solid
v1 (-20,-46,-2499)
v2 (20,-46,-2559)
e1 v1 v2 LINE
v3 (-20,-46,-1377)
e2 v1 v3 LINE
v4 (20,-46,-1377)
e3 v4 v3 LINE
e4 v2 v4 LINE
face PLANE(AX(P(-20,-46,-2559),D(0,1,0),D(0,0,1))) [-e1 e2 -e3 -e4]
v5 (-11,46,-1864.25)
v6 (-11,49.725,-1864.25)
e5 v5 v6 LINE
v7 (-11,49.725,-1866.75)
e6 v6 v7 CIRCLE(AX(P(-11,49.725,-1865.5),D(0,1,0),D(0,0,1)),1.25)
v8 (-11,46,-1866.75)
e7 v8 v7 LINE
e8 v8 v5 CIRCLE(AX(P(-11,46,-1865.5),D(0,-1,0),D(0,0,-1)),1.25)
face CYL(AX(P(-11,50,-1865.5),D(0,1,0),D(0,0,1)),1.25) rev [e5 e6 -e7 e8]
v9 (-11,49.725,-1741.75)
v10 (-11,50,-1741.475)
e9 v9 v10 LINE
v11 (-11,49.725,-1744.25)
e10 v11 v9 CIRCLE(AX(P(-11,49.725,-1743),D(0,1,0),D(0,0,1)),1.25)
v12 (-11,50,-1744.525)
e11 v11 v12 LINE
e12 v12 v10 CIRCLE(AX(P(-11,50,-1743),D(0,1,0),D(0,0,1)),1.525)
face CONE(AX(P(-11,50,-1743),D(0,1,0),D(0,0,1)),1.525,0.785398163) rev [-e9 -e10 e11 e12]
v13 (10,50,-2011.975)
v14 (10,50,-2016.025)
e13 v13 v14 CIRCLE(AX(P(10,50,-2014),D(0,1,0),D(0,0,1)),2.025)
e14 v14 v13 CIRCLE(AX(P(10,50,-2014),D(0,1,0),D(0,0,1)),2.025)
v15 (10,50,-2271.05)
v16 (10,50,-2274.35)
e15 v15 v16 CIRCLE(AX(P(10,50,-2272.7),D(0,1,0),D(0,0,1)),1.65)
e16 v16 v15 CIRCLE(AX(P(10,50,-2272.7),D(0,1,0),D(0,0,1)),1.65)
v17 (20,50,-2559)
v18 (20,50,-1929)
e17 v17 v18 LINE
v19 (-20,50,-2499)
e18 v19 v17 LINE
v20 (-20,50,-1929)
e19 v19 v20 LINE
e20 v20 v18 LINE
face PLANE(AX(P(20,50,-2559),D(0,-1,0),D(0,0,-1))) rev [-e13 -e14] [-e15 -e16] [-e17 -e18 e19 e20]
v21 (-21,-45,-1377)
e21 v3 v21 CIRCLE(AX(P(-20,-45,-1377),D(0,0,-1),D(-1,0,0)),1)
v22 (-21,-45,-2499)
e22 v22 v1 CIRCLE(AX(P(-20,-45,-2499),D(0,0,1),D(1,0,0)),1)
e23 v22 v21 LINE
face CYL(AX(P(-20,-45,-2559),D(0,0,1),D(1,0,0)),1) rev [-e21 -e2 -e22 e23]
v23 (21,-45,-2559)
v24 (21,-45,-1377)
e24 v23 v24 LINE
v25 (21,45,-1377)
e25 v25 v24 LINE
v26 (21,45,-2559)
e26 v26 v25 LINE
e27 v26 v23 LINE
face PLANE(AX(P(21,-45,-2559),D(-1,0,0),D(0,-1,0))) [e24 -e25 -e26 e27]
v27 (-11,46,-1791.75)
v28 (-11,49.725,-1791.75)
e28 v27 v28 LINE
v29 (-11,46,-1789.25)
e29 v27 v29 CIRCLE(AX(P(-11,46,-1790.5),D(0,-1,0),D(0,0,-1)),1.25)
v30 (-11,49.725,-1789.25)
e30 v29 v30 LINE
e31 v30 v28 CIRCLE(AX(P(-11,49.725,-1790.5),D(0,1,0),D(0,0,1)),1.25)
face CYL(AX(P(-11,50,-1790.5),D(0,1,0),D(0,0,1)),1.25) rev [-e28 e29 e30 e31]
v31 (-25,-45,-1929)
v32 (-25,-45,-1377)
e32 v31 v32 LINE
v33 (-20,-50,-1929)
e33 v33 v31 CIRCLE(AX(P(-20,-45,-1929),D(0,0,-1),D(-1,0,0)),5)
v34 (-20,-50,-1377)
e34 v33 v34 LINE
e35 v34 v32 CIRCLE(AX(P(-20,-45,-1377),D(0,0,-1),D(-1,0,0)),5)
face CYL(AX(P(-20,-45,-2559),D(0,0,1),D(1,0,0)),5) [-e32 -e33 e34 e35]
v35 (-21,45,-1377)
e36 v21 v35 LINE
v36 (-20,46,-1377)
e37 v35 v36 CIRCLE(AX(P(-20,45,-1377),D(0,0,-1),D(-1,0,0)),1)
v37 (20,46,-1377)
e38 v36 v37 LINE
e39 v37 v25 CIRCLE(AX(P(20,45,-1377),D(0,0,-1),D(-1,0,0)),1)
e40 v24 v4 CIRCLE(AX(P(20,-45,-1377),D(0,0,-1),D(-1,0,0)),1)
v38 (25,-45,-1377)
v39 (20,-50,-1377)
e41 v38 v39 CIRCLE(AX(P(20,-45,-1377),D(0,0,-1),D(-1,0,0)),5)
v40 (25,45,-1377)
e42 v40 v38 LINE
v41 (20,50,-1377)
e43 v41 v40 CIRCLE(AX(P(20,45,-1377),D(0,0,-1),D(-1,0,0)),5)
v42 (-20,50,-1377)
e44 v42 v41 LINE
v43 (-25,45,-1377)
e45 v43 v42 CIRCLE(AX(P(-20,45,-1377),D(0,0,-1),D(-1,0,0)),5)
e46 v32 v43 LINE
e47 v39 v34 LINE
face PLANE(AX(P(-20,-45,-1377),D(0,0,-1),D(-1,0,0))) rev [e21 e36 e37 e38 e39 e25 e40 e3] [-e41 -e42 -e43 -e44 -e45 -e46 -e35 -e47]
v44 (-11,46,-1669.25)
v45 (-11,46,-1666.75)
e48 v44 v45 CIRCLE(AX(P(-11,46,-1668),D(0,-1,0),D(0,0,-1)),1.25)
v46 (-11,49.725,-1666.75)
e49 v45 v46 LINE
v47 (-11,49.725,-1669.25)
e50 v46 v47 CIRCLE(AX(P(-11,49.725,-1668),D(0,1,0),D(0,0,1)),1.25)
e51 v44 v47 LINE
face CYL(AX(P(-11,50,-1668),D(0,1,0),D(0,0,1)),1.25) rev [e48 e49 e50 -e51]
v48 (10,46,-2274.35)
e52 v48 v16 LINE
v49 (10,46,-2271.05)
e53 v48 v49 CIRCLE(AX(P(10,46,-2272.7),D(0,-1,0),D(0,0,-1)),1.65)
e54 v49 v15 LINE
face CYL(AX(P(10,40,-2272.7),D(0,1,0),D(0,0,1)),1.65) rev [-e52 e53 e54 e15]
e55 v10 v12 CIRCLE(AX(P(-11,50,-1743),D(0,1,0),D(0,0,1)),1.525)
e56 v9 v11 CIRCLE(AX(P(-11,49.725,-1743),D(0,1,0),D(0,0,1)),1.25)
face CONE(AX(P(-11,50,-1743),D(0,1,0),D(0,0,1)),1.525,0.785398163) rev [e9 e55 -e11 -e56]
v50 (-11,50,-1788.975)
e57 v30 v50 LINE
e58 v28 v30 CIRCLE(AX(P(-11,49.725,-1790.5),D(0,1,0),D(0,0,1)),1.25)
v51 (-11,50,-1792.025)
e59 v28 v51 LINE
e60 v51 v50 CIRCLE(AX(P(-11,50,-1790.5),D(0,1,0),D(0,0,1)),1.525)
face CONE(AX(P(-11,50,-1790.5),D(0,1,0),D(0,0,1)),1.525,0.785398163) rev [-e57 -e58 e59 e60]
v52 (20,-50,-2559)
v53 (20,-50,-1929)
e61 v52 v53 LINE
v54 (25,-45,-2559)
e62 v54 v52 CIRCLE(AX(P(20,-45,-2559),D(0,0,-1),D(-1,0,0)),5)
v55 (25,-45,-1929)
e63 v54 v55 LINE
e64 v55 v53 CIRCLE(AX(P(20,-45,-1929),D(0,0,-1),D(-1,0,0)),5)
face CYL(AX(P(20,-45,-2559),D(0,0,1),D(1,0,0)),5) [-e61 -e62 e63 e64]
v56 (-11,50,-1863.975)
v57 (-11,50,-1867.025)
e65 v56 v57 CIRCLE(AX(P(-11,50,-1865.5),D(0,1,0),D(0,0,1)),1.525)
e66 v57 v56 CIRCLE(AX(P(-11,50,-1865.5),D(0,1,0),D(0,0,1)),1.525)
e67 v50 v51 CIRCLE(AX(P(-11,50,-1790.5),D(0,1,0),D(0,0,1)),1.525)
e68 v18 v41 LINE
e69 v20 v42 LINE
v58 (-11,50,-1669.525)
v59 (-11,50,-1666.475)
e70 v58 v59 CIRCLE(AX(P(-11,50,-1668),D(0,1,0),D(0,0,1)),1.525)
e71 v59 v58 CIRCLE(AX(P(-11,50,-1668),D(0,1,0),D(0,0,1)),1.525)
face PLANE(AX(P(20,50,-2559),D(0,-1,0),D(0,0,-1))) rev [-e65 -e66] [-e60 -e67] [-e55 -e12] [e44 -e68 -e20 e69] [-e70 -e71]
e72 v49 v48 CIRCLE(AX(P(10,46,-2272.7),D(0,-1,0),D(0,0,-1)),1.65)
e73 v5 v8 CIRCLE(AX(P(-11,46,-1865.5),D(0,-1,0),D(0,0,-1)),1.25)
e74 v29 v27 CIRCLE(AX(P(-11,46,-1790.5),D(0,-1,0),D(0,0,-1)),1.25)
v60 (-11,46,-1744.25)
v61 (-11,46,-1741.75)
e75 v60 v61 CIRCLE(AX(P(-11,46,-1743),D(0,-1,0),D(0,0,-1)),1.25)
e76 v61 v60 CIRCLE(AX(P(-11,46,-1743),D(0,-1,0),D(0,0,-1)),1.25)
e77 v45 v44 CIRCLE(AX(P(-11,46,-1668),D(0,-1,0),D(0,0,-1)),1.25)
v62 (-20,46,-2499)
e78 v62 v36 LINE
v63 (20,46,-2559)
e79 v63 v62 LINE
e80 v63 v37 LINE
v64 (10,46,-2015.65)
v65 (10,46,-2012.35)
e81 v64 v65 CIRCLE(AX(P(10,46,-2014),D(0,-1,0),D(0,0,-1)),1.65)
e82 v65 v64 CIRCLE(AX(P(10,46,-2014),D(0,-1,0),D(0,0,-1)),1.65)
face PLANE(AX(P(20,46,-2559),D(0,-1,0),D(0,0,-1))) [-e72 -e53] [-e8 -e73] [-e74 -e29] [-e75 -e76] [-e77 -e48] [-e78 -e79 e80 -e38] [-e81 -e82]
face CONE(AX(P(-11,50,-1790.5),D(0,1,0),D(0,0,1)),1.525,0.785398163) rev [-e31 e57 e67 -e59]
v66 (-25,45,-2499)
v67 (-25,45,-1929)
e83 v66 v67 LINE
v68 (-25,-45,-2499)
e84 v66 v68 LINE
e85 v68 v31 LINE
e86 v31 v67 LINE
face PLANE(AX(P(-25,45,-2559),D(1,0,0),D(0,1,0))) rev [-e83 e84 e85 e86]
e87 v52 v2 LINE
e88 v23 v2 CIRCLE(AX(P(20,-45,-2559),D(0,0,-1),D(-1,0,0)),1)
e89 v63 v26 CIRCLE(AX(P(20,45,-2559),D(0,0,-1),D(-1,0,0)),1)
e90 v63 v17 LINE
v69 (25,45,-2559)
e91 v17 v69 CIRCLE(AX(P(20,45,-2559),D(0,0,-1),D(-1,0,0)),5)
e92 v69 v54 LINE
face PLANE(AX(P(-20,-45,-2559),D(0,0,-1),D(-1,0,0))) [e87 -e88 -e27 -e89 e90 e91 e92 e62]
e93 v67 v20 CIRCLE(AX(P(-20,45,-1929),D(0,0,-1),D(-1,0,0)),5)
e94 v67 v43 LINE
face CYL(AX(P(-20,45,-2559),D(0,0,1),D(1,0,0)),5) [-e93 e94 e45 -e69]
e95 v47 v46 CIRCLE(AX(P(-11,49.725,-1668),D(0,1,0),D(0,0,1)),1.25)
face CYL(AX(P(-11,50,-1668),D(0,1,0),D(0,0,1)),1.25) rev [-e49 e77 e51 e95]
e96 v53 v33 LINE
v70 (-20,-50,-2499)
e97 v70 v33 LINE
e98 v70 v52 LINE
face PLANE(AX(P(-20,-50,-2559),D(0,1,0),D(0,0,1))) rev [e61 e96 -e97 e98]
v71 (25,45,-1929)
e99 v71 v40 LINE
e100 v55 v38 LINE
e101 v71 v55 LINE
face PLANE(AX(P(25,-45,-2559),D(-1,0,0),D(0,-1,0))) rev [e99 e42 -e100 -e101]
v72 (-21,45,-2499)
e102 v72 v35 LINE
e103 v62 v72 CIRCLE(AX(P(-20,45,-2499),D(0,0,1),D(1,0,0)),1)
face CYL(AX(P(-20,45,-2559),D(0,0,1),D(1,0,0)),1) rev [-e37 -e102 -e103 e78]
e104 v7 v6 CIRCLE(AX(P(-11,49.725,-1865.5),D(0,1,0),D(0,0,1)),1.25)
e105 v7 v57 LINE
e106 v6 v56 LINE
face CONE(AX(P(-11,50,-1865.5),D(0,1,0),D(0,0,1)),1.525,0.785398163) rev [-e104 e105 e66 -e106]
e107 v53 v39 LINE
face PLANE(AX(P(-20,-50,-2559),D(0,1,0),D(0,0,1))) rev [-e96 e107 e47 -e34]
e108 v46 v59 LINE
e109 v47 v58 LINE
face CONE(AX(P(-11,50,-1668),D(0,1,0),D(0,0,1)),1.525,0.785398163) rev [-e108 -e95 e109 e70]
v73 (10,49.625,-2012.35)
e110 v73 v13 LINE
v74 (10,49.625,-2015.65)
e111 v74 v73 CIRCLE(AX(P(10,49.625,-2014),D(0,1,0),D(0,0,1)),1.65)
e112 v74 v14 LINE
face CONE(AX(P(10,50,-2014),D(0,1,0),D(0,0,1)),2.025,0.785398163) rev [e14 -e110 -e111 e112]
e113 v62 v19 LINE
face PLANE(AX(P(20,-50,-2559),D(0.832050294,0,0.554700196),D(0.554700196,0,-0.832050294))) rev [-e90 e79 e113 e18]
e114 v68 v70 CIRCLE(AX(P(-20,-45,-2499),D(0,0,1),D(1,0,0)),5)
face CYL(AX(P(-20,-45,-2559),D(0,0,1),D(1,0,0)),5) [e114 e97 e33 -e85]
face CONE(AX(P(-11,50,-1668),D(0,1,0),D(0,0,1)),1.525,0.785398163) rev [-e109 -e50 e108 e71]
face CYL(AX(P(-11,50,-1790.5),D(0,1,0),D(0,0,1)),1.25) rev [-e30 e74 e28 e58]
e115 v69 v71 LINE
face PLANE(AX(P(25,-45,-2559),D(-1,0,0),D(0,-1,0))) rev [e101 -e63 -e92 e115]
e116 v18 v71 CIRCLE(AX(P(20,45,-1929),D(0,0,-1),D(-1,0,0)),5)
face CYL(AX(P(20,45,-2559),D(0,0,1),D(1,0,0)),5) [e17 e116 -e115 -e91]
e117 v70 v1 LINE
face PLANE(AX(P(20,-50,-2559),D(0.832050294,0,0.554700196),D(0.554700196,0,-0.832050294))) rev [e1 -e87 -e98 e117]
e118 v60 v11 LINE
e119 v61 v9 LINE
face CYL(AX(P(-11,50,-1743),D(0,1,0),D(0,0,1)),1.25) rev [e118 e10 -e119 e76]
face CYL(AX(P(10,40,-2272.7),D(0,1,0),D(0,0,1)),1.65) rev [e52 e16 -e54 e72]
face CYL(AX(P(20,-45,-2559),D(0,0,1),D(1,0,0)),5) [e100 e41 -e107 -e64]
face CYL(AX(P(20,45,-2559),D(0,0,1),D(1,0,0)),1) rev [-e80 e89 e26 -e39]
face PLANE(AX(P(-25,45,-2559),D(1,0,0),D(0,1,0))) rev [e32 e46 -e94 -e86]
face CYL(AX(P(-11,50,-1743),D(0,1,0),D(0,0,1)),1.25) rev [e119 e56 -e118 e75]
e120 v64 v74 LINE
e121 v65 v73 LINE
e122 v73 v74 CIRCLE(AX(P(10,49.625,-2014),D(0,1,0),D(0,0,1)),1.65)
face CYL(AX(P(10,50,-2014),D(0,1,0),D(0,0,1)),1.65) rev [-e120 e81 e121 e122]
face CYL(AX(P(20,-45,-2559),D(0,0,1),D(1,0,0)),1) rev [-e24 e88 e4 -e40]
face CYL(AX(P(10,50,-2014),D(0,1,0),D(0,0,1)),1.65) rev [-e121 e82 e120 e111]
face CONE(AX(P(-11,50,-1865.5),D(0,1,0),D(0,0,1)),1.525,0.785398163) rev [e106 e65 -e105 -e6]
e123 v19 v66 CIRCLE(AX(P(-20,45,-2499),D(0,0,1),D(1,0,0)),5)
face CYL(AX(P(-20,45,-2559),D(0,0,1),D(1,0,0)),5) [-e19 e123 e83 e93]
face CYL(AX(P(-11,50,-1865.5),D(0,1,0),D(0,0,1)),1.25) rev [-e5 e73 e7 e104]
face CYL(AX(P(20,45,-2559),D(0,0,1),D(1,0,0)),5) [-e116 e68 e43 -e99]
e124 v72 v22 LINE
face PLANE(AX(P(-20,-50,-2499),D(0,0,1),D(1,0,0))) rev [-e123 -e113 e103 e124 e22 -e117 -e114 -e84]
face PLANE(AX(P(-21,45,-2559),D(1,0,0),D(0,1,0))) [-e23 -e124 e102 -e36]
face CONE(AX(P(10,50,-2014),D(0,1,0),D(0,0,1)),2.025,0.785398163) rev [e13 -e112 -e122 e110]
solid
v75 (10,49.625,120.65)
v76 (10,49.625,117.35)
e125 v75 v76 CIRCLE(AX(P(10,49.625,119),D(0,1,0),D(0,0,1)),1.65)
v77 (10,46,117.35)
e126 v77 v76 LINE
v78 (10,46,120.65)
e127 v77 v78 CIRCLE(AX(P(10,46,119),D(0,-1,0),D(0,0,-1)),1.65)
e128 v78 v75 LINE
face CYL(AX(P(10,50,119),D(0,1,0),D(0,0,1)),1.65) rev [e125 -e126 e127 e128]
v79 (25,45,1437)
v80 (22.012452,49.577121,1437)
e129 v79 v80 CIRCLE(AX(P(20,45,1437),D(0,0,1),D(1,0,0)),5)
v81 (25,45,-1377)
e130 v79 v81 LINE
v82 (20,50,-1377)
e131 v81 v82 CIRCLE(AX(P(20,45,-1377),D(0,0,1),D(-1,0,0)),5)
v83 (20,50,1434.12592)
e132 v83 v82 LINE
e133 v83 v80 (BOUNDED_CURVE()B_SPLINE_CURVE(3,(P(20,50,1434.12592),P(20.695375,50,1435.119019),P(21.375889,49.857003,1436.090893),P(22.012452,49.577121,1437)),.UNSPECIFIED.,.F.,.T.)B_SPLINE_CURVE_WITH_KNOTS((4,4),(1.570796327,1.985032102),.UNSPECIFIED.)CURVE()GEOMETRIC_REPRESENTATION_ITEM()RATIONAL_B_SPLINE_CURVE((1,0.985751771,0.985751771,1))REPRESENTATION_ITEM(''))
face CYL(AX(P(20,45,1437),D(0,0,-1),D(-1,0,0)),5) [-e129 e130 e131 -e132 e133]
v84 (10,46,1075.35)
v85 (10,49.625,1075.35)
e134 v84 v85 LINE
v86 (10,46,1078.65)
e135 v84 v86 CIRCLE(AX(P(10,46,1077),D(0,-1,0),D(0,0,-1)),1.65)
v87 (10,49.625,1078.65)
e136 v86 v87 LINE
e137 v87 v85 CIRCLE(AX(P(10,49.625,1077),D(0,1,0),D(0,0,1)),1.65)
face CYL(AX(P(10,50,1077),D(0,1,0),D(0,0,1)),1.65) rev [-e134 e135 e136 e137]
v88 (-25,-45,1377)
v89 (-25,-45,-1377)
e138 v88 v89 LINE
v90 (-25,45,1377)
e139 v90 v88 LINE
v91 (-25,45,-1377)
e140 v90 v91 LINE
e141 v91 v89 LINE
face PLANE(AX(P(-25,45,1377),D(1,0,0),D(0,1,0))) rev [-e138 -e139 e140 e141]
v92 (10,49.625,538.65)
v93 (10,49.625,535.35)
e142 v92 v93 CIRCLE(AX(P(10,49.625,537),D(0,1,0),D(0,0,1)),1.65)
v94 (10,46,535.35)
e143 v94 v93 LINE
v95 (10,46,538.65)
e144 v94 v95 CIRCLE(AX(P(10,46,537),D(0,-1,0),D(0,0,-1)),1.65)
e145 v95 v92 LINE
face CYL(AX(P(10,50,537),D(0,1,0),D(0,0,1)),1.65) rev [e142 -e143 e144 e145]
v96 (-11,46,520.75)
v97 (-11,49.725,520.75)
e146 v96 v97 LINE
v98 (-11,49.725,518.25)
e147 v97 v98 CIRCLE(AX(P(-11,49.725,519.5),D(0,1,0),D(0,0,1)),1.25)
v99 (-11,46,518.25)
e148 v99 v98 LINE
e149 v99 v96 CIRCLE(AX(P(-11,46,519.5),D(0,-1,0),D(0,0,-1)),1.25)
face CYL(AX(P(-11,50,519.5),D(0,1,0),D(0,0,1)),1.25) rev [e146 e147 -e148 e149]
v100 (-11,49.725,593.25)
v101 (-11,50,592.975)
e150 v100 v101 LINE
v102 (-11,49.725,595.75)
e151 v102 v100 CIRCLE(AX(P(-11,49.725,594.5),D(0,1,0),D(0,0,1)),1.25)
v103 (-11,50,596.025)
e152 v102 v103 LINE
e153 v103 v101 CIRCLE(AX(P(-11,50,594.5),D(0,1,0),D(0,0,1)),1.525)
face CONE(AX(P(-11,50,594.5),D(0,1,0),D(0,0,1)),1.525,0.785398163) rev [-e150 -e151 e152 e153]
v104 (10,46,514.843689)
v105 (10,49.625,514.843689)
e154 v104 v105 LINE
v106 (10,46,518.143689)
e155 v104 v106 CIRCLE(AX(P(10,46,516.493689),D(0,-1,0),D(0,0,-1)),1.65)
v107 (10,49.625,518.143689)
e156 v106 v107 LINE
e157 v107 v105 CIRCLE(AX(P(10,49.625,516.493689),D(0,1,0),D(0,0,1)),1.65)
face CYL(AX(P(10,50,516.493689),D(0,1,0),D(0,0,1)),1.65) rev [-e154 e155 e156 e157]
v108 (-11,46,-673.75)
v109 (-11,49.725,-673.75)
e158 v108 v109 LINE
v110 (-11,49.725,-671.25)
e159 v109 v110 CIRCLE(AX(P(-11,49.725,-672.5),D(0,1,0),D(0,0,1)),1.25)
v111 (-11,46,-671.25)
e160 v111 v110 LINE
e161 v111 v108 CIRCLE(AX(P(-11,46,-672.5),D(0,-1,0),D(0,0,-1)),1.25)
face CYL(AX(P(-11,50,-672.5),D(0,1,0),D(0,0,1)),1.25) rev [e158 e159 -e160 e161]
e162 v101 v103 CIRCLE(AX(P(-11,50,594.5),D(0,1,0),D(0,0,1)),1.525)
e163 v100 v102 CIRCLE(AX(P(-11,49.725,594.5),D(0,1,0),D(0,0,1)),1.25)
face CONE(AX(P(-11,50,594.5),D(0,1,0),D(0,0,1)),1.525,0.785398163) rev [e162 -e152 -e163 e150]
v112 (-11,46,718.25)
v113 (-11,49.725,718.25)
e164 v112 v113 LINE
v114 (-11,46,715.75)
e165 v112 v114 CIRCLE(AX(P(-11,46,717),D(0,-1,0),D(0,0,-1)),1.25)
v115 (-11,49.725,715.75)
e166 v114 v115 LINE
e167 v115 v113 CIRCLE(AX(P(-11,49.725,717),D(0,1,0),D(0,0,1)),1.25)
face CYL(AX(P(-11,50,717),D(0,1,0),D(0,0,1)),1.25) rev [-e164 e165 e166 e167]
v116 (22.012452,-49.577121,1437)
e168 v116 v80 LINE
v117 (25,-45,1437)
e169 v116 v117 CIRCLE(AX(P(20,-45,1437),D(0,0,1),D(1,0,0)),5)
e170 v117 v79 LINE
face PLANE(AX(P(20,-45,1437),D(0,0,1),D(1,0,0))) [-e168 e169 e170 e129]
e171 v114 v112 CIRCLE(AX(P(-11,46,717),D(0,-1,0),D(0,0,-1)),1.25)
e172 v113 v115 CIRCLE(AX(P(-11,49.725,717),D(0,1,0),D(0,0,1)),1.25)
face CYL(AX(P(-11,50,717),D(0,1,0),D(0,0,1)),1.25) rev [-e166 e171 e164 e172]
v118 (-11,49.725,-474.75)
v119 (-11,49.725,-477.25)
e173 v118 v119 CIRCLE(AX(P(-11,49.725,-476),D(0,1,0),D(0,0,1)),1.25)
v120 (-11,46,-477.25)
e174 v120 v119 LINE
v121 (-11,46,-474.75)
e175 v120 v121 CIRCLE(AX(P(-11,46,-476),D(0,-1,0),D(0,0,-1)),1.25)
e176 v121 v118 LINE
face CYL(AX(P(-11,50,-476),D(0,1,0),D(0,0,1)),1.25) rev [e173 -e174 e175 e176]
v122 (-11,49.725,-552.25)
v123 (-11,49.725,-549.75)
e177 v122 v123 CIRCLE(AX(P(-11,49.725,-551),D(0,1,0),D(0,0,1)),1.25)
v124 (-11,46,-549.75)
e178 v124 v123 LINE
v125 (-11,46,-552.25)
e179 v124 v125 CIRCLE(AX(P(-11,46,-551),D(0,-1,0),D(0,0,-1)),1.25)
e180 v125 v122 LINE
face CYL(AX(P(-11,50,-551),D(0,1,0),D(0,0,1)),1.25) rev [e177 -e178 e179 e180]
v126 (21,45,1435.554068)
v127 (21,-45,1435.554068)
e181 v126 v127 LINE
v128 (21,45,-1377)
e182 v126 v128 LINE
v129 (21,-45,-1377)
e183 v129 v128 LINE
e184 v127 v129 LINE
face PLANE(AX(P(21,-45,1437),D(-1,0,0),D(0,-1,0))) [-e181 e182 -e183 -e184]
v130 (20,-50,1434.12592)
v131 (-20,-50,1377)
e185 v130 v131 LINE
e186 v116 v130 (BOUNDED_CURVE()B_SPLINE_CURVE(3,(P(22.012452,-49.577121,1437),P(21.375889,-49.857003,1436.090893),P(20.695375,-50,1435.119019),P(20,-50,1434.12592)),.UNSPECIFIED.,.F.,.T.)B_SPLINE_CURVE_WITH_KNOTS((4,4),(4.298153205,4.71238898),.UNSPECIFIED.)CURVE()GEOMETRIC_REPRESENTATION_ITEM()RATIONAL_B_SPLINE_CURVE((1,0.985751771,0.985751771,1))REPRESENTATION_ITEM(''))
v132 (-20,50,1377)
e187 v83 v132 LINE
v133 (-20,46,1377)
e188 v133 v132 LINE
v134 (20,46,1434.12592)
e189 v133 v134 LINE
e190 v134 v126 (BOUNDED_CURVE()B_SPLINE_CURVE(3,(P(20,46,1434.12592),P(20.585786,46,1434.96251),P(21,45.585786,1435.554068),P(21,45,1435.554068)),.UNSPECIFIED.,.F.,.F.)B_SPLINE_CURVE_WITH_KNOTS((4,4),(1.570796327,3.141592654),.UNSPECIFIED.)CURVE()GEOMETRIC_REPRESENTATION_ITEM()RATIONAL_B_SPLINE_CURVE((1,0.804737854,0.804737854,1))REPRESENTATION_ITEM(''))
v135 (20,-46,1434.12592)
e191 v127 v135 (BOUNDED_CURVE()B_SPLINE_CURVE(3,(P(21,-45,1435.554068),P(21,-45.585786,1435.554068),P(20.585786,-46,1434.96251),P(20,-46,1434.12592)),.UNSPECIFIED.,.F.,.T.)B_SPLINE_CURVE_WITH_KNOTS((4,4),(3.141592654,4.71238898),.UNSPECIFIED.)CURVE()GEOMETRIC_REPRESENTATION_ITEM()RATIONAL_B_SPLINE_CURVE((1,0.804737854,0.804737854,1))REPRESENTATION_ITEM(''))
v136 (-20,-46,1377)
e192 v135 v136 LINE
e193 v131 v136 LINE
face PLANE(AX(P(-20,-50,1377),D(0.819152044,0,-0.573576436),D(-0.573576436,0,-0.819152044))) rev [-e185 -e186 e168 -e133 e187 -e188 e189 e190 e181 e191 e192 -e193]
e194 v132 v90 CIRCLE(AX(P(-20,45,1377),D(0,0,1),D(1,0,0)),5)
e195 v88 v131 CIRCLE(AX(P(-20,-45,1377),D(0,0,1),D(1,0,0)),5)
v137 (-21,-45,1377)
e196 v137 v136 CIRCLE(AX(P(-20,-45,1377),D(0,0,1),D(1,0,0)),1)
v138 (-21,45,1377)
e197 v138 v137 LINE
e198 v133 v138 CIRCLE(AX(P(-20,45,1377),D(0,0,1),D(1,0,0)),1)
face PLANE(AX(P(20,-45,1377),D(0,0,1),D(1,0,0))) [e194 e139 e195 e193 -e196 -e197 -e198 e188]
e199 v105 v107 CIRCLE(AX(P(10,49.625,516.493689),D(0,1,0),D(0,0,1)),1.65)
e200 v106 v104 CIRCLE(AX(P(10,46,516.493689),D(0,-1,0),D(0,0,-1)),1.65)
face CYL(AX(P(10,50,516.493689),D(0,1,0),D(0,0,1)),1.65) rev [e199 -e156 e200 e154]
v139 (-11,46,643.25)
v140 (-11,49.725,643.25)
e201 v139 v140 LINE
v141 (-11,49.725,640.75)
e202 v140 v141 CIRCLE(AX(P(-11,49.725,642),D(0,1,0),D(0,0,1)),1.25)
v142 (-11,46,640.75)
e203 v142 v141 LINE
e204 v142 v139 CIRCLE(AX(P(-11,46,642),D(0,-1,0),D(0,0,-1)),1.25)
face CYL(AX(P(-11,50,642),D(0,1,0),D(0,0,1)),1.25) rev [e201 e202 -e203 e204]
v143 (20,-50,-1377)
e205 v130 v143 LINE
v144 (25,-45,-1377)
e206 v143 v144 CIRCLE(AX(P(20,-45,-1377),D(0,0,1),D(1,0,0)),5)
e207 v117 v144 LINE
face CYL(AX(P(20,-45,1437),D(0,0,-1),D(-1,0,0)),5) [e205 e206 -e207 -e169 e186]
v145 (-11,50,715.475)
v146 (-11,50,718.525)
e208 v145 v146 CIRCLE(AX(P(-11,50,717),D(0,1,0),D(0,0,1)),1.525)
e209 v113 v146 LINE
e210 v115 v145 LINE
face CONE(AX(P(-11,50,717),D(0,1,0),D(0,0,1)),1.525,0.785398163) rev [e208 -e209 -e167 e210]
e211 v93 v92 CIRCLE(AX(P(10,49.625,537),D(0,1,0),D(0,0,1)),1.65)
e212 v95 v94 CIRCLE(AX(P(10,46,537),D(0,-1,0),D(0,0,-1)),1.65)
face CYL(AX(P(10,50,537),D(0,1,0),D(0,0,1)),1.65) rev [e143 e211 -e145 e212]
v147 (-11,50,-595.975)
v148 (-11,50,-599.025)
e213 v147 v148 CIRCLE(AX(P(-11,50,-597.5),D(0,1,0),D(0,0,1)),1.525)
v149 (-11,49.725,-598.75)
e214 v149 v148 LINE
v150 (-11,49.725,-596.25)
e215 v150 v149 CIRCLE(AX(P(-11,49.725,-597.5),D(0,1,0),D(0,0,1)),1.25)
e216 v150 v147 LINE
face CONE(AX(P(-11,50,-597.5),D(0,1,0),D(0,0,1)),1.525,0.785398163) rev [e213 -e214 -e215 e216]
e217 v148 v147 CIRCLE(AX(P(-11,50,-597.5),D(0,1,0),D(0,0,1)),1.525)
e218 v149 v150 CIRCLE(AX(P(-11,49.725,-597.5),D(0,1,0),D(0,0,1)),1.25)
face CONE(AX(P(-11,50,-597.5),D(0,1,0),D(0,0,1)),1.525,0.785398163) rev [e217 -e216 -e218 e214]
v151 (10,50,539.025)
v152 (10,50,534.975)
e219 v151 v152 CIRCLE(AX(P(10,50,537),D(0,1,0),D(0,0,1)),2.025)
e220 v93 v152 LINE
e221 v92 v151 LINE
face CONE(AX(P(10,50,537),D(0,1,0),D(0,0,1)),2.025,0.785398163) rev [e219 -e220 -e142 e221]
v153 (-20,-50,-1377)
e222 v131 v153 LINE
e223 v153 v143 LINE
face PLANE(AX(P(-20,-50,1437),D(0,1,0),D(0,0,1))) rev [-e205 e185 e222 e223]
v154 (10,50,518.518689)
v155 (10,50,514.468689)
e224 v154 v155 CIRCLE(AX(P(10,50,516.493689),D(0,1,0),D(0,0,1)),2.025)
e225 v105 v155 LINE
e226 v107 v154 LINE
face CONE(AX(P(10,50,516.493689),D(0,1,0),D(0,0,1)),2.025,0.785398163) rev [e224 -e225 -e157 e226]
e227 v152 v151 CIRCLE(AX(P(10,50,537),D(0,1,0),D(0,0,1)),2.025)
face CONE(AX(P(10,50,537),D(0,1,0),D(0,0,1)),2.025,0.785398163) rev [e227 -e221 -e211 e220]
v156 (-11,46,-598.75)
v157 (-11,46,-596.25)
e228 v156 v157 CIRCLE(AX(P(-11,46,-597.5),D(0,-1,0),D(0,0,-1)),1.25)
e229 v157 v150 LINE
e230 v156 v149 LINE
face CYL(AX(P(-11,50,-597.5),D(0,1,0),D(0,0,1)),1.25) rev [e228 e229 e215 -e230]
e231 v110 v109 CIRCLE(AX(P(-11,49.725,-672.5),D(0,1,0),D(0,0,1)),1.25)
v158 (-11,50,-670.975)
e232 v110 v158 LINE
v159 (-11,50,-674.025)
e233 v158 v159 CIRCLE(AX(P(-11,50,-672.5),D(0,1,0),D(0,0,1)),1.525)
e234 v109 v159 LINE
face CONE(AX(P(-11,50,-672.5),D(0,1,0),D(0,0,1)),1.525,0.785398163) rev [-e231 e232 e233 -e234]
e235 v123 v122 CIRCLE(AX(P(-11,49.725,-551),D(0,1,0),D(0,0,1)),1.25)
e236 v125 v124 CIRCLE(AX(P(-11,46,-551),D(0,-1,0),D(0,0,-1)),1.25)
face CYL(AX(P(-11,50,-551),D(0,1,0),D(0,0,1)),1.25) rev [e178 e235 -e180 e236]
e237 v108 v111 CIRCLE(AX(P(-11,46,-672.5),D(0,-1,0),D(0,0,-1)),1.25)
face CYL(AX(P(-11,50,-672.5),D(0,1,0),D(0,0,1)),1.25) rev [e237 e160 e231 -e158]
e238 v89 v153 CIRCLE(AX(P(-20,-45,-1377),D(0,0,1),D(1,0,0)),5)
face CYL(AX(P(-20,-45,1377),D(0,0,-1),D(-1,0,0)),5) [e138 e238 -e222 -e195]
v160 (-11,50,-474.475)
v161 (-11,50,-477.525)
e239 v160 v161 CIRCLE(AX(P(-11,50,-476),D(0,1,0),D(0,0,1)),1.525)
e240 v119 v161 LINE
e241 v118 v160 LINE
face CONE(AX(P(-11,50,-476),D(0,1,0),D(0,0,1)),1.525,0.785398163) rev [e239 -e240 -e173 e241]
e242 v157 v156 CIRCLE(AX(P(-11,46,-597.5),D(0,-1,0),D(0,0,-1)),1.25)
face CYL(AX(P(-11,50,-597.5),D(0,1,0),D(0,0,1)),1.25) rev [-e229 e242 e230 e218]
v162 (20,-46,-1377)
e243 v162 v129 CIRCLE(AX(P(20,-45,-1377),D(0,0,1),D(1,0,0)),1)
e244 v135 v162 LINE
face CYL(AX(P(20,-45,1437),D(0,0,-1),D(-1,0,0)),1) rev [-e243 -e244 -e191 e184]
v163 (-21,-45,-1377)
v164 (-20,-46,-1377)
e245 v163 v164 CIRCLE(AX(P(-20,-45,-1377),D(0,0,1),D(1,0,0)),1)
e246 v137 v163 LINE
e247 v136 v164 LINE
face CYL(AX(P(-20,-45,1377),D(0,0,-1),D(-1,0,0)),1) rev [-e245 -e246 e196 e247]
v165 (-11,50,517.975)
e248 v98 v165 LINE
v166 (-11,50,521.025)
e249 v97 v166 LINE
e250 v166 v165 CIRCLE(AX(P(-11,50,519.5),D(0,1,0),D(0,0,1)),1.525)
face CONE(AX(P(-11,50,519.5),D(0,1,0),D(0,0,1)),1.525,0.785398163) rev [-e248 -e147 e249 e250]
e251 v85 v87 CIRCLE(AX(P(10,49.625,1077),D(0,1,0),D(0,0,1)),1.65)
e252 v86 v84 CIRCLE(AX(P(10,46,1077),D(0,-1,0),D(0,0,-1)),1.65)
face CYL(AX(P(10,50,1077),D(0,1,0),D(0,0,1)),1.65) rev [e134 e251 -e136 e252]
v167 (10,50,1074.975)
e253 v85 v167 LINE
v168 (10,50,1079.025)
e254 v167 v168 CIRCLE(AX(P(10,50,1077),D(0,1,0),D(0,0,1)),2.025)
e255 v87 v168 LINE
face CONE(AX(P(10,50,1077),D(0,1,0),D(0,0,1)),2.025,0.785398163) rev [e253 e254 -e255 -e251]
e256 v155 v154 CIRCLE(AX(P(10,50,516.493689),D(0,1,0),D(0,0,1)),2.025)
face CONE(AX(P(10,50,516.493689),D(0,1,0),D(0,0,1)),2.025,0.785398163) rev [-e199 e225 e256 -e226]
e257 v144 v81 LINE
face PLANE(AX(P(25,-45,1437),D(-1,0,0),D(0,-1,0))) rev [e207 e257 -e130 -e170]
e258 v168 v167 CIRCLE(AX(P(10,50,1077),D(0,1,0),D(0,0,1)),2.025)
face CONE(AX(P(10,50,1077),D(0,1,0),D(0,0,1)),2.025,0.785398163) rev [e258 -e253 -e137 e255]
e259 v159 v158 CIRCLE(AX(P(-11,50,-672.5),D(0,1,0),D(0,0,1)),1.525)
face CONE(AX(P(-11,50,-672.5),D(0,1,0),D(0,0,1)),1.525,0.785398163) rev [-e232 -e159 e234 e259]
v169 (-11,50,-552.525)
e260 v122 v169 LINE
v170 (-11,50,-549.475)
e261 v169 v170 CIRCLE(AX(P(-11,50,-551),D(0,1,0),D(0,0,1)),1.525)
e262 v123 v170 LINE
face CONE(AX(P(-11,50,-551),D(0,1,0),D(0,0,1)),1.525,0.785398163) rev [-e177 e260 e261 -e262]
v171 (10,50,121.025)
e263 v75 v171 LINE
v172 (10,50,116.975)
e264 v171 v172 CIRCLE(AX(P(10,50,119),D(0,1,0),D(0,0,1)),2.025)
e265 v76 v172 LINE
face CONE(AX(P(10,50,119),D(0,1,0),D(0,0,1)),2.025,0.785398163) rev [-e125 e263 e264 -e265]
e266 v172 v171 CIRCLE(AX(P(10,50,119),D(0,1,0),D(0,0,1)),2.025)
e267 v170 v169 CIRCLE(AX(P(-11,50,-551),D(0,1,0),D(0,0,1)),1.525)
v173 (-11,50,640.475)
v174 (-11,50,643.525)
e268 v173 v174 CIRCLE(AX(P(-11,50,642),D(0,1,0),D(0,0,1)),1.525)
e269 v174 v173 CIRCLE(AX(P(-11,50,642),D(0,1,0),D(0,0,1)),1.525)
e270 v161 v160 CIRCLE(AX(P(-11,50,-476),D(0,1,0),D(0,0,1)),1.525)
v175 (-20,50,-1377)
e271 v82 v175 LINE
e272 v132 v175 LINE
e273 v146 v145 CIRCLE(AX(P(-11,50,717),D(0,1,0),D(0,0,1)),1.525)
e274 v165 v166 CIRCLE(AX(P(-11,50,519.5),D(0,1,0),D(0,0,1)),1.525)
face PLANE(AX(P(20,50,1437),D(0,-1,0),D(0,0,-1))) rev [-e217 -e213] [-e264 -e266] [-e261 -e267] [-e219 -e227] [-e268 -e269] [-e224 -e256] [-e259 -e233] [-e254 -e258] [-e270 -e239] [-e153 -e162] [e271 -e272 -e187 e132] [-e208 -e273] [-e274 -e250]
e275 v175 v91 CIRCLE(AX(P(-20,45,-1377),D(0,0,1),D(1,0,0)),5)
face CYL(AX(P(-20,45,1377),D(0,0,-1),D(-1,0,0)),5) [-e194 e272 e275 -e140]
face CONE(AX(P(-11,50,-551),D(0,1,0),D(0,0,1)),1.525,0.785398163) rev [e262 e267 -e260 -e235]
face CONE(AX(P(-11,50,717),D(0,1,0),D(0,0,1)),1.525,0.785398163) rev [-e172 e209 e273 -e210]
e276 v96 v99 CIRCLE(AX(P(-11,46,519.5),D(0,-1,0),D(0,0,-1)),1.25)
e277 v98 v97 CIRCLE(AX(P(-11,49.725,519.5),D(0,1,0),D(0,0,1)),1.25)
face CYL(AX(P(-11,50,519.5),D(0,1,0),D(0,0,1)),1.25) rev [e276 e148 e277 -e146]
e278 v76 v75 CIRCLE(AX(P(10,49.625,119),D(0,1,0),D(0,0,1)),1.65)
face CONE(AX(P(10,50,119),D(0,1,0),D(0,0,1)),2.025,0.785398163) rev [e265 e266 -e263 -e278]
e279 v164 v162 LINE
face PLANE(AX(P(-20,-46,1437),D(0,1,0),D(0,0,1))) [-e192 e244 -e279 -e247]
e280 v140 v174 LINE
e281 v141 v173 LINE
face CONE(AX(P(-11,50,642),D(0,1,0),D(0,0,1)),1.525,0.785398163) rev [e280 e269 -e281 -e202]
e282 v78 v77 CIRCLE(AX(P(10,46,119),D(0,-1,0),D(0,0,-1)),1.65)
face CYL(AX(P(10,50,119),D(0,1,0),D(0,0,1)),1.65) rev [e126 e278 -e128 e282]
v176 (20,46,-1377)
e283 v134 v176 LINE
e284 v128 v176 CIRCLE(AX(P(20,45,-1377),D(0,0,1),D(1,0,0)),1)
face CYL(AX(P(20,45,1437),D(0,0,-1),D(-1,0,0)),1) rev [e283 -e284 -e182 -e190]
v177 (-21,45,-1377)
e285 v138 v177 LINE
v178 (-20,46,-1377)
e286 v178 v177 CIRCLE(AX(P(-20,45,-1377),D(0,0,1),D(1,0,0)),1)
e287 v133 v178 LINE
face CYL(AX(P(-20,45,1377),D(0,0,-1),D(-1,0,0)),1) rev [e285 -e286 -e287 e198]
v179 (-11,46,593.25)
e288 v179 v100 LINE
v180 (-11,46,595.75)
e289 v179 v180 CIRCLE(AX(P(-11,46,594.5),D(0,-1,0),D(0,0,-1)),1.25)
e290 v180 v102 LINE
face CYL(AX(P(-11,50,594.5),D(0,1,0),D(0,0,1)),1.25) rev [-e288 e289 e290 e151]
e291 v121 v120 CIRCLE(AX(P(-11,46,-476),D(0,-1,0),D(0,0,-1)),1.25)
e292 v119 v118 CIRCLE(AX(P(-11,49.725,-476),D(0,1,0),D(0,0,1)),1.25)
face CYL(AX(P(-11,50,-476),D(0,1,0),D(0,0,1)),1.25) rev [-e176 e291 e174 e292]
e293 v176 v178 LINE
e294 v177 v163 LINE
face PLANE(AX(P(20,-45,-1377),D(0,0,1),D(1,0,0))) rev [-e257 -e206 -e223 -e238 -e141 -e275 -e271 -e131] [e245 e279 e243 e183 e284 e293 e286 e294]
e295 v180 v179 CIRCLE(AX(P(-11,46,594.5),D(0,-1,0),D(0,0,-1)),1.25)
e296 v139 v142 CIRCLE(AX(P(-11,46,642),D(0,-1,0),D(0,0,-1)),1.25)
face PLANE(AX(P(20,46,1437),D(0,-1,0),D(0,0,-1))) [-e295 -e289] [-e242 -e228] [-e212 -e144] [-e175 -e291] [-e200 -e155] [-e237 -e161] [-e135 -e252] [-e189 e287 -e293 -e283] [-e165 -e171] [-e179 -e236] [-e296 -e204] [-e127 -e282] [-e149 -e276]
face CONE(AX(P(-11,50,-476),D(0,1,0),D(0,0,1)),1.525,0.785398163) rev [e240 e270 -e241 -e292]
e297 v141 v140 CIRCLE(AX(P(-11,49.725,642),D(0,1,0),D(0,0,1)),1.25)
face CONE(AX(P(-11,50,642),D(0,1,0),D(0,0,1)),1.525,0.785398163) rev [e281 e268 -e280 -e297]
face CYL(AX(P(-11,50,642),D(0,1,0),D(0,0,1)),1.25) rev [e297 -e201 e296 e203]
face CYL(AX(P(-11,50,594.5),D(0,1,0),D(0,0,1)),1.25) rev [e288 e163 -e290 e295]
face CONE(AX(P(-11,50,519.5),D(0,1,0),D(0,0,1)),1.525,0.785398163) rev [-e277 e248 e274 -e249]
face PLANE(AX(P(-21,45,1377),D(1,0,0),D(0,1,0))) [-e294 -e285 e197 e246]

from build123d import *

# Parameters (mm, degrees)
EXTRUDE_1_DEPTH              = 1377
EXTRUDE_1_2_DEPTH            = 60
CUT_EXTRUDE_1_DEPTH          = 1441.692194745
EXTRUDE_2_DEPTH              = 1182
CUT_EXTRUDE_2_DEPTH          = 2562.075164848
HOLE_WIZARD_M3_1_AT_2_COUNT  = 2
HOLE_WIZARD_M3_1_AT_2_PITCH  = 2507.499999999
HOLE_WIZARD_M3_1_AT_3_COUNT  = 2
HOLE_WIZARD_M3_1_AT_3_PITCH  = 2582.499999999
HOLE_WIZARD_M3_1_AT_4_COUNT  = 2
HOLE_WIZARD_M3_1_AT_4_PITCH  = 2459.999999999
HOLE_WIZARD_M3_1_AT_5_COUNT  = 2
HOLE_WIZARD_M3_1_AT_5_PITCH  = 2384.999999999
HOLE_WIZARD_M3_1_AT_6_COUNT  = 2
HOLE_WIZARD_M3_1_AT_6_PITCH  = 1389.5
HOLE_WIZARD_M3_1_AT_7_COUNT  = 2
HOLE_WIZARD_M3_1_AT_7_PITCH  = 1314.5
HOLE_WIZARD_M3_1_AT_8_COUNT  = 2
HOLE_WIZARD_M3_1_AT_8_PITCH  = 1268
HOLE_WIZARD_M3_1_AT_9_COUNT  = 2
HOLE_WIZARD_M3_1_AT_9_PITCH  = 1193
HOLE_WIZARD_M3_1_AT_10_COUNT = 2
HOLE_WIZARD_M3_1_AT_10_PITCH = 122.5
HOLE_WIZARD_M3_1_AT_11_COUNT = 2
HOLE_WIZARD_M3_1_AT_11_PITCH = 197.5
HOLE_WIZARD_M3_1_AT_12_COUNT = 2
HOLE_WIZARD_M3_1_AT_12_PITCH = 75
HOLE_WIZARD_M4_2_AT_2_COUNT  = 2
HOLE_WIZARD_M4_2_AT_2_PITCH  = 397.493689191
HOLE_WIZARD_M4_2_AT_3_COUNT  = 2
HOLE_WIZARD_M4_2_AT_3_PITCH  = 418
HOLE_WIZARD_M4_2_AT_4_COUNT  = 2
HOLE_WIZARD_M4_2_AT_4_PITCH  = 958
SKETCH_14_R                  = 1.65
CUT_EXTRUDE_3_DEPTH          = 10


with BuildPart() as part:
    # 草图1 → Extrude 1 (new, symmetric)
    with BuildSketch(Plane.XY):
        with BuildLine():
            Line((-20, 50), (20, 50))
            ThreePointArc((20, 50), (23.535533906, 48.535533906), (25, 45))
            Line((25, 45), (25, -45))
            ThreePointArc((25, -45), (23.535533906, -48.535533906), (20, -50))
            Line((20, -50), (-20, -50))
            ThreePointArc((-20, -50), (-23.535533906, -48.535533906), (-25, -45))
            Line((-25, -45), (-25, 45))
            ThreePointArc((-25, 45), (-23.535533906, 48.535533906), (-20, 50))
        make_face()
        with BuildLine():
            Line((-20, 46), (20, 46))
            ThreePointArc((20, 46), (20.707106781, 45.707106781), (21, 45))
            Line((21, 45), (21, -45))
            ThreePointArc((21, -45), (20.707106781, -45.707106781), (20, -46))
            Line((20, -46), (-20, -46))
            ThreePointArc((-20, -46), (-20.707106781, -45.707106781), (-21, -45))
            Line((-21, -45), (-21, 45))
            ThreePointArc((-21, 45), (-20.707106781, 45.707106781), (-20, 46))
        make_face(mode=Mode.SUBTRACT)
    extrude(amount=EXTRUDE_1_DEPTH, both=True)


with BuildPart() as body_2:
    # 草图2 → Extrude 1 2 (new body)
    with BuildSketch(Plane.XY.offset(1377)):
        with BuildLine():
            Line((-20, -50), (20, -50))
            ThreePointArc((20, -50), (23.535533906, -48.535533906), (25, -45))
            Line((25, -45), (25, 45))
            ThreePointArc((25, 45), (23.535533906, 48.535533906), (20, 50))
            Line((20, 50), (-20, 50))
            ThreePointArc((-20, 50), (-23.535533906, 48.535533906), (-25, 45))
            Line((-25, 45), (-25, -45))
            ThreePointArc((-25, -45), (-23.535533906, -48.535533906), (-20, -50))
        make_face()
        with BuildLine():
            Line((-20, -46), (20, -46))
            ThreePointArc((20, -46), (20.707106781, -45.707106781), (21, -45))
            Line((21, -45), (21, 45))
            ThreePointArc((21, 45), (20.707106781, 45.707106781), (20, 46))
            Line((20, 46), (-20, 46))
            ThreePointArc((-20, 46), (-20.707106781, 45.707106781), (-21, 45))
            Line((-21, 45), (-21, -45))
            ThreePointArc((-21, -45), (-20.707106781, -45.707106781), (-20, -46))
        make_face(mode=Mode.SUBTRACT)
    extrude(amount=EXTRUDE_1_2_DEPTH)

    # 草图3 → 切除-拉伸1 (cut, through all)
    with BuildSketch(Plane(origin=(0, 50, 0), x_dir=(1, 0, 0), z_dir=(0, 1, 0))):
        Polygon((-20, -1377), (22.012452293, -1437), (-44.133254367, -1437), (-44.133254367, -1377), align=None)
    extrude(amount=-CUT_EXTRUDE_1_DEPTH, mode=Mode.SUBTRACT)


with BuildPart() as body_3:
    # 草图4 → 凸台-拉伸2 (new body)
    with BuildSketch(Plane(origin=(0, 0, -1377), x_dir=(-1, 0, 0), z_dir=(0, 0, -1))):
        with BuildLine():
            Line((20, -50), (-20, -50))
            ThreePointArc((-20, -50), (-23.535533906, -48.535533906), (-25, -45))
            Line((-25, -45), (-25, 45))
            ThreePointArc((-25, 45), (-23.535533906, 48.535533906), (-20, 50))
            Line((-20, 50), (20, 50))
            ThreePointArc((20, 50), (23.535533906, 48.535533906), (25, 45))
            Line((25, 45), (25, -45))
            ThreePointArc((25, -45), (23.535533906, -48.535533906), (20, -50))
        make_face()
        with BuildLine():
            Line((20, -46), (-20, -46))
            ThreePointArc((-20, -46), (-20.707106781, -45.707106781), (-21, -45))
            Line((-21, -45), (-21, 45))
            ThreePointArc((-21, 45), (-20.707106781, 45.707106781), (-20, 46))
            Line((-20, 46), (20, 46))
            ThreePointArc((20, 46), (20.707106781, 45.707106781), (21, 45))
            Line((21, 45), (21, -45))
            ThreePointArc((21, -45), (20.707106781, -45.707106781), (20, -46))
        make_face(mode=Mode.SUBTRACT)
    extrude(amount=EXTRUDE_2_DEPTH)

    # 草图5 → 切除-拉伸2 (cut, through all)
    with BuildSketch(Plane(origin=(0, 50, 0), x_dir=(1, 0, 0), z_dir=(0, 1, 0))):
        Polygon((20, 2559), (-20, 2499), (-29.87796777, 2499), (-29.87796777, 2930.227490927), (20, 2930.227490927), align=None)
    extrude(amount=-CUT_EXTRUDE_2_DEPTH, mode=Mode.SUBTRACT)

    # 草图8 → M3 螺纹孔1 (revolve, cut)
    with BuildSketch(Plane(origin=(-11, 50, -1865.499999999), x_dir=(0, 0, 1), z_dir=(1, 0, 0))):
        Polygon((0, 0), (0, 9.251075774), (1.25, 8.5), (1.25, 0.275), (1.525, 0), align=None)
    hole_wizard_m3_1 = revolve(axis=Axis((-11, 56.35, -1865.499999999), (0, -1, 0)), mode=Mode.SUBTRACT)

    # M3 螺纹孔1 at 10: M3 螺纹孔1 ×2
    with Locations(*[(0, 0, i * HOLE_WIZARD_M3_1_AT_10_PITCH) for i in range(1, HOLE_WIZARD_M3_1_AT_10_COUNT)]):
        add(hole_wizard_m3_1, mode=Mode.SUBTRACT)

    # M3 螺纹孔1 at 11: M3 螺纹孔1 ×2
    with Locations(*[(0, 0, i * HOLE_WIZARD_M3_1_AT_11_PITCH) for i in range(1, HOLE_WIZARD_M3_1_AT_11_COUNT)]):
        add(hole_wizard_m3_1, mode=Mode.SUBTRACT)

    # M3 螺纹孔1 at 12: M3 螺纹孔1 ×2
    with Locations(*[(0, 0, i * HOLE_WIZARD_M3_1_AT_12_PITCH) for i in range(1, HOLE_WIZARD_M3_1_AT_12_COUNT)]):
        add(hole_wizard_m3_1, mode=Mode.SUBTRACT)

    # 草图13 → M4 螺纹孔3 (revolve, cut)
    with BuildSketch(Plane(origin=(10, 50, -2014), x_dir=(0, 0, 1), z_dir=(1, 0, 0))):
        Polygon((0, 0), (0, 11.091420021), (1.65, 10.1), (1.65, 0.375), (2.025, 0), align=None)
    revolve(axis=Axis((10, 56.35, -2014), (0, -1, 0)), mode=Mode.SUBTRACT)

    # 草图14 → 切除-拉伸3 (cut)
    with BuildSketch(Plane(origin=(0, 50, 0), x_dir=(1, 0, 0), z_dir=(0, 1, 0))):
        with Locations(Location((10, 2272.7, 0), (0, 0, 270))):
            Circle(SKETCH_14_R)
    extrude(amount=-CUT_EXTRUDE_3_DEPTH, mode=Mode.SUBTRACT)


with BuildPart() as part_1:
    add(part.part)

    # M3 螺纹孔1 at 2: M3 螺纹孔1 ×2
    with Locations(*[(0, 0, i * HOLE_WIZARD_M3_1_AT_2_PITCH) for i in range(1, HOLE_WIZARD_M3_1_AT_2_COUNT)]):
        add(hole_wizard_m3_1, mode=Mode.SUBTRACT)

    # M3 螺纹孔1 at 3: M3 螺纹孔1 ×2
    with Locations(*[(0, 0, i * HOLE_WIZARD_M3_1_AT_3_PITCH) for i in range(1, HOLE_WIZARD_M3_1_AT_3_COUNT)]):
        add(hole_wizard_m3_1, mode=Mode.SUBTRACT)

    # M3 螺纹孔1 at 4: M3 螺纹孔1 ×2
    with Locations(*[(0, 0, i * HOLE_WIZARD_M3_1_AT_4_PITCH) for i in range(1, HOLE_WIZARD_M3_1_AT_4_COUNT)]):
        add(hole_wizard_m3_1, mode=Mode.SUBTRACT)

    # M3 螺纹孔1 at 5: M3 螺纹孔1 ×2
    with Locations(*[(0, 0, i * HOLE_WIZARD_M3_1_AT_5_PITCH) for i in range(1, HOLE_WIZARD_M3_1_AT_5_COUNT)]):
        add(hole_wizard_m3_1, mode=Mode.SUBTRACT)

    # M3 螺纹孔1 at 6: M3 螺纹孔1 ×2
    with Locations(*[(0, 0, i * HOLE_WIZARD_M3_1_AT_6_PITCH) for i in range(1, HOLE_WIZARD_M3_1_AT_6_COUNT)]):
        add(hole_wizard_m3_1, mode=Mode.SUBTRACT)

    # M3 螺纹孔1 at 7: M3 螺纹孔1 ×2
    with Locations(*[(0, 0, i * HOLE_WIZARD_M3_1_AT_7_PITCH) for i in range(1, HOLE_WIZARD_M3_1_AT_7_COUNT)]):
        add(hole_wizard_m3_1, mode=Mode.SUBTRACT)

    # M3 螺纹孔1 at 8: M3 螺纹孔1 ×2
    with Locations(*[(0, 0, i * HOLE_WIZARD_M3_1_AT_8_PITCH) for i in range(1, HOLE_WIZARD_M3_1_AT_8_COUNT)]):
        add(hole_wizard_m3_1, mode=Mode.SUBTRACT)

    # M3 螺纹孔1 at 9: M3 螺纹孔1 ×2
    with Locations(*[(0, 0, i * HOLE_WIZARD_M3_1_AT_9_PITCH) for i in range(1, HOLE_WIZARD_M3_1_AT_9_COUNT)]):
        add(hole_wizard_m3_1, mode=Mode.SUBTRACT)

    # 草图11 → M4 螺纹孔2 (revolve, cut)
    with BuildSketch(Plane(origin=(10, 50, 119), x_dir=(0, 0, 1), z_dir=(1, 0, 0))):
        Polygon((0, 0), (0, 11.091420021), (1.65, 10.1), (1.65, 0.375), (2.025, 0), align=None)
    hole_wizard_m4_2 = revolve(axis=Axis((10, 56.35, 119), (0, -1, 0)), mode=Mode.SUBTRACT)

    # M4 螺纹孔2 at 2: M4 螺纹孔2 ×2
    with Locations(*[(0, 0, i * HOLE_WIZARD_M4_2_AT_2_PITCH) for i in range(1, HOLE_WIZARD_M4_2_AT_2_COUNT)]):
        add(hole_wizard_m4_2, mode=Mode.SUBTRACT)

    # M4 螺纹孔2 at 3: M4 螺纹孔2 ×2
    with Locations(*[(0, 0, i * HOLE_WIZARD_M4_2_AT_3_PITCH) for i in range(1, HOLE_WIZARD_M4_2_AT_3_COUNT)]):
        add(hole_wizard_m4_2, mode=Mode.SUBTRACT)

    # M4 螺纹孔2 at 4: M4 螺纹孔2 ×2
    with Locations(*[(0, 0, i * HOLE_WIZARD_M4_2_AT_4_PITCH) for i in range(1, HOLE_WIZARD_M4_2_AT_4_COUNT)]):
        add(hole_wizard_m4_2, mode=Mode.SUBTRACT)


with BuildPart() as body_2_1:
    add(body_2.part)

    # Combine 1: union part
    add(part_1.part)


solid = Compound([body_3.part, body_2_1.part])
